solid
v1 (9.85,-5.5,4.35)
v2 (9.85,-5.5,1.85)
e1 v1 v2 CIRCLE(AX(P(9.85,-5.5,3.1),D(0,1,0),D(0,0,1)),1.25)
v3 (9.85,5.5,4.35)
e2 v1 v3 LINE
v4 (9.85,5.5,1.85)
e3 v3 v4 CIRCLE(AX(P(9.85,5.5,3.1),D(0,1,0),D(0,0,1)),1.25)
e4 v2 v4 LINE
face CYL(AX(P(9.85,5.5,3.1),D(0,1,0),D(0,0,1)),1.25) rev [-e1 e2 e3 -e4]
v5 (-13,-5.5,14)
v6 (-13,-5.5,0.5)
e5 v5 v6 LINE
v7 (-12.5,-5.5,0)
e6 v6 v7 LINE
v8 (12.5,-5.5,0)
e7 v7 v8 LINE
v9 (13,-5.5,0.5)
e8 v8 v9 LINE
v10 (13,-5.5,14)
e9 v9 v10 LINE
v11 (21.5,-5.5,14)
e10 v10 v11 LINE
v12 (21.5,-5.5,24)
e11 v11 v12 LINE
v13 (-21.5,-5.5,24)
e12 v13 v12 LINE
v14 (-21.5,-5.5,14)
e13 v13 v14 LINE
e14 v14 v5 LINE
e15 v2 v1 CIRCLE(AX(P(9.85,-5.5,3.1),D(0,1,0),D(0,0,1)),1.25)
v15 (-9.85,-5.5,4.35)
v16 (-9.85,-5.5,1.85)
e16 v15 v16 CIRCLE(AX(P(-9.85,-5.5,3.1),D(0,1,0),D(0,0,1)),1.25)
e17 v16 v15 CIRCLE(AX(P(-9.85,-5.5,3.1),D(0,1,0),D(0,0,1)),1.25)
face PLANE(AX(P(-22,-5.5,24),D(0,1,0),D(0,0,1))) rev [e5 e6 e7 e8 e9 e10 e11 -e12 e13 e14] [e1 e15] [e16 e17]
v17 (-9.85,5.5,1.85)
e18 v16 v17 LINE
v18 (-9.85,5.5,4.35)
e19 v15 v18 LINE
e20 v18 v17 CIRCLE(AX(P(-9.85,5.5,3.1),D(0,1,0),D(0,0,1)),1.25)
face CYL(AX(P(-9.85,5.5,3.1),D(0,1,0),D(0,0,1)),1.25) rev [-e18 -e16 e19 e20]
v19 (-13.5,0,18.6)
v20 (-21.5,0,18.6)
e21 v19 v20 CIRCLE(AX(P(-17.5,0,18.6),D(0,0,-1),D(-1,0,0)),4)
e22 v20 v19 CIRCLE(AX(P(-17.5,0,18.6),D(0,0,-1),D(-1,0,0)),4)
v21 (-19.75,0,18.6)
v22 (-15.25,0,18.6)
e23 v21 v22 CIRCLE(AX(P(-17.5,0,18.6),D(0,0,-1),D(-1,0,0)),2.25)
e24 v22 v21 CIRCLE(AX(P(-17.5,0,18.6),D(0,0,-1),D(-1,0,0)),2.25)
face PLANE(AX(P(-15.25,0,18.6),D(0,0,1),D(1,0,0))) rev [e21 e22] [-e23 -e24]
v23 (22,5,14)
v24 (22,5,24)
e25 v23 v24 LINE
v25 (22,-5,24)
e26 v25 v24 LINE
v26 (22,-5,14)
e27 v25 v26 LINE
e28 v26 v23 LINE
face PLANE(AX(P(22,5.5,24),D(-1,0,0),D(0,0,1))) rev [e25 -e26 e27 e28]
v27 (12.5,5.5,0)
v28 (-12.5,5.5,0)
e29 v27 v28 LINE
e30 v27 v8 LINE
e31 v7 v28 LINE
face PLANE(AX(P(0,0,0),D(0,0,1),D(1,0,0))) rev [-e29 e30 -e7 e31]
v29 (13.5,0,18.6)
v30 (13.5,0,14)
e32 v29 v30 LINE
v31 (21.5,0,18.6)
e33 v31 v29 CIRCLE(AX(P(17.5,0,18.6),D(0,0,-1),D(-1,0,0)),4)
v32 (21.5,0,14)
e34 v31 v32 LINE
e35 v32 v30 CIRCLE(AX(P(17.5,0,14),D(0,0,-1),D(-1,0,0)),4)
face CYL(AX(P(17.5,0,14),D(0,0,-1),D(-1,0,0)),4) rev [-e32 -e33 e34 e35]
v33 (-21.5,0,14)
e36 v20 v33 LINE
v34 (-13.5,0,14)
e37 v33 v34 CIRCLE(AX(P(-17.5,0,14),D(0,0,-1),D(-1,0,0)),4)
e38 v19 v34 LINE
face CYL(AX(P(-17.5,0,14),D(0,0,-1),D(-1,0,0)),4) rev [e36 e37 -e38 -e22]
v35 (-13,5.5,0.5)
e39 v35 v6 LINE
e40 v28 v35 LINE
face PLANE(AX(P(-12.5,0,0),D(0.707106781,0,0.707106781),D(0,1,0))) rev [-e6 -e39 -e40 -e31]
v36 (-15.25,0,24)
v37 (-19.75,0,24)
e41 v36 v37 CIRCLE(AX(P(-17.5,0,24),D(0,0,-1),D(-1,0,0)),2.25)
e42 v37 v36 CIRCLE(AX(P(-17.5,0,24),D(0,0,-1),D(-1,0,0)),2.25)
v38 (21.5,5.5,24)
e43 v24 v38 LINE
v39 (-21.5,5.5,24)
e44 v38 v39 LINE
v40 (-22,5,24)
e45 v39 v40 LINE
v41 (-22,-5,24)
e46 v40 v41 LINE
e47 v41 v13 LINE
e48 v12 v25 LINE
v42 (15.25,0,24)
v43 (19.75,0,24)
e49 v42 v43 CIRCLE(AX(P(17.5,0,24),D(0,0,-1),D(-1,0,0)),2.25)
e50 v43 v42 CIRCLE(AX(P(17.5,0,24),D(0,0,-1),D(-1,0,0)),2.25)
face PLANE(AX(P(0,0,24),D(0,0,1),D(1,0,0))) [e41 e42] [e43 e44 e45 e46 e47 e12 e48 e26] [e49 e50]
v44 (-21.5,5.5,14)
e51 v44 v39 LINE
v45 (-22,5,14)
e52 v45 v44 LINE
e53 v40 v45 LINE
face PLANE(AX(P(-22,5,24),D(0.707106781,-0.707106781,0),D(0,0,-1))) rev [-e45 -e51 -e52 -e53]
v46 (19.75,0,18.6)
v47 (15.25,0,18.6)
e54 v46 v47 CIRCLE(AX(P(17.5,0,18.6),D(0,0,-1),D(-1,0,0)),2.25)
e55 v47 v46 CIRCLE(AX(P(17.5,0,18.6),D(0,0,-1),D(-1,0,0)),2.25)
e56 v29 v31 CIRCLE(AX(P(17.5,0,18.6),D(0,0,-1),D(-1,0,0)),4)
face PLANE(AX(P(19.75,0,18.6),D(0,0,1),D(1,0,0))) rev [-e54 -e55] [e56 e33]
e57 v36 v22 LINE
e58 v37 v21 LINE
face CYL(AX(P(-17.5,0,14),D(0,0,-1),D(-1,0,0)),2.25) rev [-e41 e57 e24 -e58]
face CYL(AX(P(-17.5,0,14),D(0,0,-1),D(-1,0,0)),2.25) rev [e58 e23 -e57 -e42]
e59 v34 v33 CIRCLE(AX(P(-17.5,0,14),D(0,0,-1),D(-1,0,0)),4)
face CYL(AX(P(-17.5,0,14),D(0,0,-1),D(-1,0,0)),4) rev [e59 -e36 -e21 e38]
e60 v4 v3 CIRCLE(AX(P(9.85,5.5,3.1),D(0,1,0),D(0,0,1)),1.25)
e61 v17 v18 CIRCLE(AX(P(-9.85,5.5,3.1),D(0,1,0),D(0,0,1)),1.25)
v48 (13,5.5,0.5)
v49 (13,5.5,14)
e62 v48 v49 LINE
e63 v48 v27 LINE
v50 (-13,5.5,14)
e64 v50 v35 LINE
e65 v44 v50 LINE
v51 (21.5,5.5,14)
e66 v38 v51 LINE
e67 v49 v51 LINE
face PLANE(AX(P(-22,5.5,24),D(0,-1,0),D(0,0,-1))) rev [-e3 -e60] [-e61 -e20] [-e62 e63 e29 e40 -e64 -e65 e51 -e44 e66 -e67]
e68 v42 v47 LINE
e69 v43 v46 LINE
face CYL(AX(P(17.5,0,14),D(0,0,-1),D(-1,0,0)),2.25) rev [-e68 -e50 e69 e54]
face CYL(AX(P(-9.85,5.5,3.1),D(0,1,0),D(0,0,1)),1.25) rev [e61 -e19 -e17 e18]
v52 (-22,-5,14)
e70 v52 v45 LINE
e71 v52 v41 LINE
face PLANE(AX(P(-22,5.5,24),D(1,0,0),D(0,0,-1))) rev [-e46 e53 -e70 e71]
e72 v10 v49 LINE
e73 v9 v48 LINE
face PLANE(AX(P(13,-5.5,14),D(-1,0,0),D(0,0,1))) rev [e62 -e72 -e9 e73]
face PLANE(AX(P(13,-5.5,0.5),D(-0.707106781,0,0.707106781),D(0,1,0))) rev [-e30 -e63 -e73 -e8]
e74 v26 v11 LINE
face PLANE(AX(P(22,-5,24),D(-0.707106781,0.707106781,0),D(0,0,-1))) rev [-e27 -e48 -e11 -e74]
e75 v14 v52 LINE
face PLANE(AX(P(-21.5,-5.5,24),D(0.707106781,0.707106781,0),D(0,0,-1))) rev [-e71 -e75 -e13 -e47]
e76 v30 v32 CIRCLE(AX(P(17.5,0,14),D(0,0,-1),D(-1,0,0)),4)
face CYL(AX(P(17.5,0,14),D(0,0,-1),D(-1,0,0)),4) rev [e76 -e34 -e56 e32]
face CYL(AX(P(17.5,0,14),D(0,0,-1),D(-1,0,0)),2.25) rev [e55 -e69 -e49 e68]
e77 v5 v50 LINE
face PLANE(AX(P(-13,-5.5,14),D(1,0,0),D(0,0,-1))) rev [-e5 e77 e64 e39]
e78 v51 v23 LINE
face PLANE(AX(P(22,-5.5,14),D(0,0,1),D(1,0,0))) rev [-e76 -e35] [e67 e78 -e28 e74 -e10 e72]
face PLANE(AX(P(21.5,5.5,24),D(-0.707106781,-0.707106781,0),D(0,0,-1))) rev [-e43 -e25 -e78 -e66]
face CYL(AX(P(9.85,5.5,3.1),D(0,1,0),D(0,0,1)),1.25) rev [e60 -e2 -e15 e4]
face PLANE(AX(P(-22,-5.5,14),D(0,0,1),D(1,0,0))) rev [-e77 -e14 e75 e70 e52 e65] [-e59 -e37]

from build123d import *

# Parameters (mm, degrees)
SKETCH1_W                                            = 44
SKETCH1_H                                            = 11
BOSS_EXTRUDE1_DEPTH                                  = 24
SKETCH2_W                                            = 9
SKETCH2_H                                            = 14
CUT_EXTRUDE1_DEPTH                                   = 35.365680555
CBORE_FOR_M4_HEXAGON_SOCKET_HEAD_CAP_SCR_D           = 4.5
CBORE_FOR_M4_HEXAGON_SOCKET_HEAD_CAP_SCR_CBORE_D     = 8
CBORE_FOR_M4_HEXAGON_SOCKET_HEAD_CAP_SCR_CBORE_DEPTH = 4.6
M3_TAPPED_HOLE1_D                                    = 2.5
CHAMFER1_SIZE                                        = 0.5
CHAMFER2_SIZE                                        = 0.5


with BuildPart() as part:
    # Sketch1 → Boss-Extrude1 (new body)
    with BuildSketch(Plane.XY):
        Rectangle(SKETCH1_W, SKETCH1_H)
    extrude(amount=BOSS_EXTRUDE1_DEPTH)

    # Sketch2 → Cut-Extrude1 (cut, through all)
    with BuildSketch(Plane(origin=(0, 5.5, 0), x_dir=(1, 0, 0), z_dir=(0, 1, 0))):
        with Locations((-17.5, -7)):
            Rectangle(SKETCH2_W, SKETCH2_H)
        with Locations((17.5, -7)):
            Rectangle(SKETCH2_W, SKETCH2_H)
    extrude(amount=-CUT_EXTRUDE1_DEPTH, mode=Mode.SUBTRACT)

    # CBORE for M4 Hexagon socket head cap screws1 (through all)
    with Locations(Plane(origin=(0, 0, 14), x_dir=(-1, 0, 0), z_dir=(0, 0, -1))):
        with Locations((-17.5, 0), (17.5, 0)):
            CounterBoreHole(CBORE_FOR_M4_HEXAGON_SOCKET_HEAD_CAP_SCR_D / 2, CBORE_FOR_M4_HEXAGON_SOCKET_HEAD_CAP_SCR_CBORE_D / 2, CBORE_FOR_M4_HEXAGON_SOCKET_HEAD_CAP_SCR_CBORE_DEPTH)

    # M3 Tapped Hole1 (through all)
    with Locations(Plane(origin=(0, 5.5, 0), x_dir=(1, 0, 0), z_dir=(0, 1, 0))):
        with Locations((9.85, -3.1), (-9.85, -3.1)):
            Hole(M3_TAPPED_HOLE1_D / 2)

    # Chamfer1
    chamfer1_edges = [part.edges().sort_by_distance(p)[0] for p in [
        (22, -5.5, 19),
        (-22, -5.5, 19),
        (-22, 5.5, 19),
        (22, 5.5, 19),
    ]]
    chamfer(chamfer1_edges, length=CHAMFER1_SIZE)

    # Chamfer2
    chamfer2_edges = [part.edges().sort_by_distance(p)[0] for p in [
        (-13, 0, 0),
        (13, 0, 0),
    ]]
    chamfer(chamfer2_edges, length=CHAMFER2_SIZE)


solid = part.part
